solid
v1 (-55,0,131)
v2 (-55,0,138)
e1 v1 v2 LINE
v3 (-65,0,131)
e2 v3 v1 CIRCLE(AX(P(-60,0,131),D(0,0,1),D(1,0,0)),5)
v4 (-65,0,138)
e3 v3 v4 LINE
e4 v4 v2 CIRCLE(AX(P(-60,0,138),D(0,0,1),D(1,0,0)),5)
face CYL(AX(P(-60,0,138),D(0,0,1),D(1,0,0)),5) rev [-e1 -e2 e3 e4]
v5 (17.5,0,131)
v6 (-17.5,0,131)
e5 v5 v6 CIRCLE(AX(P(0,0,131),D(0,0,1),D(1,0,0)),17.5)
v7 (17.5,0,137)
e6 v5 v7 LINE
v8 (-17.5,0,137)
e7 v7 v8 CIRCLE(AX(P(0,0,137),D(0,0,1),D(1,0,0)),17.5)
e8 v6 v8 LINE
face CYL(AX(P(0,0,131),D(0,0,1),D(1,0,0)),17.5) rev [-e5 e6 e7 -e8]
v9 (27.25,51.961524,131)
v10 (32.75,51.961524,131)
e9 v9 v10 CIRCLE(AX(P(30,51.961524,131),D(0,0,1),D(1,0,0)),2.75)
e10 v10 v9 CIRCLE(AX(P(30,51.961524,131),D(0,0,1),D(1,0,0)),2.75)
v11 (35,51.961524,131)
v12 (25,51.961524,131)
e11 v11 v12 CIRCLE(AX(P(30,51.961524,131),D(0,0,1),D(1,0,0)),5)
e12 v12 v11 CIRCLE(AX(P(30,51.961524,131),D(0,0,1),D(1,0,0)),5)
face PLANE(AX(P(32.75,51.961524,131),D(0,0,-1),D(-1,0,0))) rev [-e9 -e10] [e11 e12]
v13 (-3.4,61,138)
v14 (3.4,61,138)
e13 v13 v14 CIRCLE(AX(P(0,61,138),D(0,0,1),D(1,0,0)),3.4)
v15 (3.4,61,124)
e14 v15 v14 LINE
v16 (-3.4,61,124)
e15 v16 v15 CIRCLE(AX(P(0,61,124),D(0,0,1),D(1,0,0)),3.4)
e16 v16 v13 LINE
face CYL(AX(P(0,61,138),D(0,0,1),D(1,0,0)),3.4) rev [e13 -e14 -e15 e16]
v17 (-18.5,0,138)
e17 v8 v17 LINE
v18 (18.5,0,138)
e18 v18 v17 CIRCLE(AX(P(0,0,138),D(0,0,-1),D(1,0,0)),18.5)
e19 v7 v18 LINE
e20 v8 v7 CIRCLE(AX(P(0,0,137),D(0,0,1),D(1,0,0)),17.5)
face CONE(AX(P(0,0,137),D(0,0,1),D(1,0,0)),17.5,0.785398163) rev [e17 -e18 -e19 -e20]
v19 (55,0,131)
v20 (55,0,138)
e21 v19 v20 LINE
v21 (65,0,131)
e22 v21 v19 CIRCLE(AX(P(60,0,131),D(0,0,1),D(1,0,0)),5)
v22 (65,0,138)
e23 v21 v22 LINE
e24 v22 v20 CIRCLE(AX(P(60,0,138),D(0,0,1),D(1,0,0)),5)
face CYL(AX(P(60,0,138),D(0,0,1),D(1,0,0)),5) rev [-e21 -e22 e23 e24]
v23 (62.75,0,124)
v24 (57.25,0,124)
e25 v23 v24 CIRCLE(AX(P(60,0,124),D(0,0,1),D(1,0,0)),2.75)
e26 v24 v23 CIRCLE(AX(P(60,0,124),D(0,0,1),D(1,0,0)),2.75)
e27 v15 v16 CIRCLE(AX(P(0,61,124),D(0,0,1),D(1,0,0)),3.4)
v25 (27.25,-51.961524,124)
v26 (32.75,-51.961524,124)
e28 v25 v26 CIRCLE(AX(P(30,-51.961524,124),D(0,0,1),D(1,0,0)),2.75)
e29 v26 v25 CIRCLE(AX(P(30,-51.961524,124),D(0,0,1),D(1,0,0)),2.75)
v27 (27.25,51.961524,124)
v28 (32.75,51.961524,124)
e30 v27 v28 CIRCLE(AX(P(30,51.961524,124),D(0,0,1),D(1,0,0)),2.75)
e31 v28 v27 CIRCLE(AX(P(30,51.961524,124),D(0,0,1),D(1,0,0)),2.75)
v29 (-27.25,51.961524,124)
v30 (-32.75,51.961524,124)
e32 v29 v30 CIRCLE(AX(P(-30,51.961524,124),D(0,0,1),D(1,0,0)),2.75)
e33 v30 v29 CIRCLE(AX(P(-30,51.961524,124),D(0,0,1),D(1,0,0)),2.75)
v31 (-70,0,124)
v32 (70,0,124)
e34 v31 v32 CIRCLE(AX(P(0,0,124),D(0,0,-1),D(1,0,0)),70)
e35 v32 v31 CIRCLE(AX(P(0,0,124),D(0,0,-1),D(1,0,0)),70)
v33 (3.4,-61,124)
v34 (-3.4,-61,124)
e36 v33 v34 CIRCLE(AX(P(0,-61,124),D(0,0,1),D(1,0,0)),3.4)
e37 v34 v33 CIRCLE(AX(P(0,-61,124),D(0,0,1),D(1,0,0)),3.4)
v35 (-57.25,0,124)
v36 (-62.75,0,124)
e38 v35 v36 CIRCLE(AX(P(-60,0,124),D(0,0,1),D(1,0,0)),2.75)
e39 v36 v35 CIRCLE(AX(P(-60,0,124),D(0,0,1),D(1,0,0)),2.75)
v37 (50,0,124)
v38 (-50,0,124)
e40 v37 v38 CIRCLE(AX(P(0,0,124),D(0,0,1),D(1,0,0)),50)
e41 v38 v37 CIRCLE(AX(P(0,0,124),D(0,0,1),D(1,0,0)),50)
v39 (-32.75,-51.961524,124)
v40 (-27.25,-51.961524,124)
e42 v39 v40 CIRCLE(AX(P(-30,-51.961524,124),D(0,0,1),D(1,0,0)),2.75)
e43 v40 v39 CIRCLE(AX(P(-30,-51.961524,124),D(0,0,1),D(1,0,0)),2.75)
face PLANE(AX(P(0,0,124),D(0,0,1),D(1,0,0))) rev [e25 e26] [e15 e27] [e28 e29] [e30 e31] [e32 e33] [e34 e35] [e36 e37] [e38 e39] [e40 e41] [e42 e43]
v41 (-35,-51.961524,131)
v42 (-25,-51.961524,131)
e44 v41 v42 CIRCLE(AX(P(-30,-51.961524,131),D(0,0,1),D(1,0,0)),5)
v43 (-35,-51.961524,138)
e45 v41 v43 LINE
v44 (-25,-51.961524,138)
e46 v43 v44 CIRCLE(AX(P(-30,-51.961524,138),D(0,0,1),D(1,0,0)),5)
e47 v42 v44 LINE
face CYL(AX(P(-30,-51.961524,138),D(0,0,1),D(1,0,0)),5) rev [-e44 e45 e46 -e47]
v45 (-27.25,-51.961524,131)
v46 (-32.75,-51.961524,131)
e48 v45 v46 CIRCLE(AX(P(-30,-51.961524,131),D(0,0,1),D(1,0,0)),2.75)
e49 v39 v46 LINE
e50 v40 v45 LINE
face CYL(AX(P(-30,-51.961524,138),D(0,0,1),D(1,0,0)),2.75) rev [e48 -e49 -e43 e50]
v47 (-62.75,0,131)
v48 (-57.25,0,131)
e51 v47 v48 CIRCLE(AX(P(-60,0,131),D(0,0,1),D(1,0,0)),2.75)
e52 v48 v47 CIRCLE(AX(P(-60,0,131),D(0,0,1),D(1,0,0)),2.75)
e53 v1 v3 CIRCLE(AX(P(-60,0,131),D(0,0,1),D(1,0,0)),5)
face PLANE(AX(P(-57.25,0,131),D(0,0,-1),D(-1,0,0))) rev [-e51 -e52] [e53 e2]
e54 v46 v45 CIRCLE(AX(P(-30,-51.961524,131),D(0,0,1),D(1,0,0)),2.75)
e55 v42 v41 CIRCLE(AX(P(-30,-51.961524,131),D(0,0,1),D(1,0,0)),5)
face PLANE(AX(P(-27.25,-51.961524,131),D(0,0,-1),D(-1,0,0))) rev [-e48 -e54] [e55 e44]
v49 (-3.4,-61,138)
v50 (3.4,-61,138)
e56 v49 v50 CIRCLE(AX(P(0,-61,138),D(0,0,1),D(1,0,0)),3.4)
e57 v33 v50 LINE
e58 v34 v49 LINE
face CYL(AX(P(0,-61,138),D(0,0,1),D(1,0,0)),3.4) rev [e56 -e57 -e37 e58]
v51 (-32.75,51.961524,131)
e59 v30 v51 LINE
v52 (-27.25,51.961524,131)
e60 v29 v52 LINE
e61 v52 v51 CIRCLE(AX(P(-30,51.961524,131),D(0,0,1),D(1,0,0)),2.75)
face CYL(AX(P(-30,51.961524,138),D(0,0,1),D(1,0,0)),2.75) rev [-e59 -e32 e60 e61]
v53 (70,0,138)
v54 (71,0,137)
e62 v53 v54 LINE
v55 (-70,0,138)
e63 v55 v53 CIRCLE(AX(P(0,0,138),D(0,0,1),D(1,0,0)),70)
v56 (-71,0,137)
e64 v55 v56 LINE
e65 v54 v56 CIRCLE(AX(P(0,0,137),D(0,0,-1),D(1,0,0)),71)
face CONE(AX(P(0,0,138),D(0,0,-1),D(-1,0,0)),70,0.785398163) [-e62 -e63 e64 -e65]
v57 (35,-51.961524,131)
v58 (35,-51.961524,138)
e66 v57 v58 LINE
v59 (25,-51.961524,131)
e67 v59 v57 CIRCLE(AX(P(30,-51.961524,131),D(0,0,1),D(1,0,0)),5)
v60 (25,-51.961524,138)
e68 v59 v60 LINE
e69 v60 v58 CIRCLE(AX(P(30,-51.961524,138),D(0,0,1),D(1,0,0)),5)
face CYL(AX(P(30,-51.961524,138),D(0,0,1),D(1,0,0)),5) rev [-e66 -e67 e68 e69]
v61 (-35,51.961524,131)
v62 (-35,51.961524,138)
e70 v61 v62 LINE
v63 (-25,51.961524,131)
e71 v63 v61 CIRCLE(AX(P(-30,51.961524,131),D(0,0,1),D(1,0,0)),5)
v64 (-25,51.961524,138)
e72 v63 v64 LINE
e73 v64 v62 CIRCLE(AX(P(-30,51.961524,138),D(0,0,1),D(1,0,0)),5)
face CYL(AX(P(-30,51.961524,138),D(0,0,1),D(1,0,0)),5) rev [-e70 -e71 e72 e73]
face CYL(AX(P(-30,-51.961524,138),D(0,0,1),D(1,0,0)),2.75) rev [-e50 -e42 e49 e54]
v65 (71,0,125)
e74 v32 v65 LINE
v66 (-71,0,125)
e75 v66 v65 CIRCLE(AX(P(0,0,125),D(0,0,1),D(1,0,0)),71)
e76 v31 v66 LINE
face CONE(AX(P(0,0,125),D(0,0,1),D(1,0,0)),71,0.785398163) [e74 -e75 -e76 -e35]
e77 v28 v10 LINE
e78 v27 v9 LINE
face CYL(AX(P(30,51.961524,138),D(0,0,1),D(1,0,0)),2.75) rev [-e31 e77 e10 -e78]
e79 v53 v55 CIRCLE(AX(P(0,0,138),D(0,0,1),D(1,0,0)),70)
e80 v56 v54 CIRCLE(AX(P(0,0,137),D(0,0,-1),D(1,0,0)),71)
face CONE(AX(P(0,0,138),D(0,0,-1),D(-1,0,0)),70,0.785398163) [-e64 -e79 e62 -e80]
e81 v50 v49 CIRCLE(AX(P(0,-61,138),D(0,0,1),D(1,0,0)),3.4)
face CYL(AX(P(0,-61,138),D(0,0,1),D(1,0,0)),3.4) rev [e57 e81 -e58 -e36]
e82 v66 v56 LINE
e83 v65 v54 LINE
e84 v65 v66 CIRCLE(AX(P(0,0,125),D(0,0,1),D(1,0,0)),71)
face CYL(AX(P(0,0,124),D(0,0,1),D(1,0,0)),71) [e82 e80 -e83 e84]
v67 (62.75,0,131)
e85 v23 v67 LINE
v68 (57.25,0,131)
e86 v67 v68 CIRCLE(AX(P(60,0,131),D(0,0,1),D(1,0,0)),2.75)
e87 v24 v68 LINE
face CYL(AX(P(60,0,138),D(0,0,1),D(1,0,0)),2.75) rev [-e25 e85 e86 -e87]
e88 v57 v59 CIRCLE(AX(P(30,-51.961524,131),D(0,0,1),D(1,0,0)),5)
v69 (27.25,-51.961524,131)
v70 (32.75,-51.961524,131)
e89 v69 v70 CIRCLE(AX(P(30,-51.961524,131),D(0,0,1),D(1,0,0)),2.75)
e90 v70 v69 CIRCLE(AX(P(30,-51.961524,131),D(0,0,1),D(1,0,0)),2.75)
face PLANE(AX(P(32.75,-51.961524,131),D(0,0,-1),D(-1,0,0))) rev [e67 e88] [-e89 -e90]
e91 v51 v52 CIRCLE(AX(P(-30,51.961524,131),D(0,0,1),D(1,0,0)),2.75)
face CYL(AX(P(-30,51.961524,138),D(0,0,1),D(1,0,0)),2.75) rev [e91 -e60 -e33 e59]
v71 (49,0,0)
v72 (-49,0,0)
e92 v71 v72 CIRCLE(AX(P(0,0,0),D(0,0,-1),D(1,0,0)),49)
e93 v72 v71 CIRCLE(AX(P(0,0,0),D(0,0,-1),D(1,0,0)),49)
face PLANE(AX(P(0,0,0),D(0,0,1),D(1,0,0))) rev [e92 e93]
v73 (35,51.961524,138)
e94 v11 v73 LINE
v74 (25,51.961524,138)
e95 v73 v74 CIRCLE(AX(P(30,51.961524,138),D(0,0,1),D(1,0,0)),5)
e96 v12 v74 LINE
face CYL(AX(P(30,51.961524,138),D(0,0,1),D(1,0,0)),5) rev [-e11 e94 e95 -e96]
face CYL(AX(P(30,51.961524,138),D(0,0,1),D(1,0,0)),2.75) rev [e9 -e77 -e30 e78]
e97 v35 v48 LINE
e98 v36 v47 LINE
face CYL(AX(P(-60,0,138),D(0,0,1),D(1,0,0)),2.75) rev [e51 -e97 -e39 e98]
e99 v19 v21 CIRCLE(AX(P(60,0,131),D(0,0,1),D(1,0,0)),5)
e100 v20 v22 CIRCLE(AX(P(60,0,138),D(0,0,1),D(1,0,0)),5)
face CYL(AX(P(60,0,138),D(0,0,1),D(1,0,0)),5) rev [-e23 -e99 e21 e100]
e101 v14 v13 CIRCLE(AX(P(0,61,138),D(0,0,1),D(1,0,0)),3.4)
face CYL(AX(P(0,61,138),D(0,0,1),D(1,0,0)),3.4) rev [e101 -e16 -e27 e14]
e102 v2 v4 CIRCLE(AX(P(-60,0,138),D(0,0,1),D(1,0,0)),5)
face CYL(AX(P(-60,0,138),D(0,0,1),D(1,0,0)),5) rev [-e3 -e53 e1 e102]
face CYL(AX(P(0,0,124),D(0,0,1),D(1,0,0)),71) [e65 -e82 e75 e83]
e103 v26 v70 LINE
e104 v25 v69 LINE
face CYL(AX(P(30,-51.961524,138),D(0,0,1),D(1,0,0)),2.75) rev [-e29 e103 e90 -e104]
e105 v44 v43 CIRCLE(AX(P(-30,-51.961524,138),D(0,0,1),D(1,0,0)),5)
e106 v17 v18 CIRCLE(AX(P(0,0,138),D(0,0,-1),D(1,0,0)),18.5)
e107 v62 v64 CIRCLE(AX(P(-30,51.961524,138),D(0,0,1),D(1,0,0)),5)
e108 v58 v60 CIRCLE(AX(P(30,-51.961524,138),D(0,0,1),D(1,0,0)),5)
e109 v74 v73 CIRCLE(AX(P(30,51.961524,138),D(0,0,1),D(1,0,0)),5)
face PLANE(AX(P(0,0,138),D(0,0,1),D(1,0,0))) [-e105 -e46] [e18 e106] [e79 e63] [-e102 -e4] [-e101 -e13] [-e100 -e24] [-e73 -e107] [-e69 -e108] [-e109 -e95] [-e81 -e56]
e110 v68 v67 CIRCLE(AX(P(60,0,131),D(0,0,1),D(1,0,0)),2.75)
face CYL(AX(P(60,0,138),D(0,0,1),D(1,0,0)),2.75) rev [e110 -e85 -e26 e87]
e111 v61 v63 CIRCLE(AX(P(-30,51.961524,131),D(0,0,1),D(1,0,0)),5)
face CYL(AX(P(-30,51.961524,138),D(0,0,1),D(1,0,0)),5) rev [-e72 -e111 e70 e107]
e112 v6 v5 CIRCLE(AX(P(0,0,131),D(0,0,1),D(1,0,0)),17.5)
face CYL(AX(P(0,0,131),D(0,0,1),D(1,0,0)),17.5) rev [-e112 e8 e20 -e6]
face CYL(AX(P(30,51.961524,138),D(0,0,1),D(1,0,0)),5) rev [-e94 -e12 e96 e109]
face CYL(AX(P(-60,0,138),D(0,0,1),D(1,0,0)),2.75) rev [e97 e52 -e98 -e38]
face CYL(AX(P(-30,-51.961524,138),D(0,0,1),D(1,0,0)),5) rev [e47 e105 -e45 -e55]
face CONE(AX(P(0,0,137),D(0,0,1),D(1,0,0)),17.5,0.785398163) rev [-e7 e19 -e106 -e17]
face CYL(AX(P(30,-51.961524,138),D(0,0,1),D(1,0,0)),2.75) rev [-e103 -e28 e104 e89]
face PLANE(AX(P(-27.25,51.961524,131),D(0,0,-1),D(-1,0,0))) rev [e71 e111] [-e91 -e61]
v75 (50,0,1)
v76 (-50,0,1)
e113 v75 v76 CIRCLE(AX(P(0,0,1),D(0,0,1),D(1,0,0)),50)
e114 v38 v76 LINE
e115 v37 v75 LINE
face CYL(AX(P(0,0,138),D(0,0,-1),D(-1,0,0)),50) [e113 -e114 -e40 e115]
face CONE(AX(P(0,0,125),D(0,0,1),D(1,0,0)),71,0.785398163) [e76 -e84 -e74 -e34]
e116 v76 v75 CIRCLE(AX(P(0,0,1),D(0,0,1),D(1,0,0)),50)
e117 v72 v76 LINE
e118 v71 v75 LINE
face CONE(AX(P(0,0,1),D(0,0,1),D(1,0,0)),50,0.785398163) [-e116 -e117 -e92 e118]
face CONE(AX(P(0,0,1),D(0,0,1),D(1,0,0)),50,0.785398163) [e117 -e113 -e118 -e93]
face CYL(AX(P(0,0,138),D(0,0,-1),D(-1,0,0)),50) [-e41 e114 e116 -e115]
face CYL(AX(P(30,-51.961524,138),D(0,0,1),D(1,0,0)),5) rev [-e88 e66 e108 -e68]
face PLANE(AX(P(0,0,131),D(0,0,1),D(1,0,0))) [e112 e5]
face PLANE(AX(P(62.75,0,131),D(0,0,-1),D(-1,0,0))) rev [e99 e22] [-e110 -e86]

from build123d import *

# Parameters (mm, degrees)
SKETCH1_R           = 50
BOSS_EXTRUDE1_DEPTH = 138
BOSS_EXTRUDE2_START = -14
SKETCH6_R           = 71
SKETCH6_R_2         = 50
BOSS_EXTRUDE2_DEPTH = 14
CHAMFER3_SIZE       = 1
CHAMFER4_SIZE       = 1
CHAMFER5_SIZE       = 1
SKETCH7_R           = 17.5
CUT_EXTRUDE1_DEPTH  = 7
CHAMFER6_SIZE       = 1
CIRPATTERN1_COUNT   = 6
M8_TAPPED_HOLE1_D   = 6.8


with BuildPart() as part:
    # Sketch1 → Boss-Extrude1 (new body)
    with BuildSketch(Plane.XY):
        Circle(SKETCH1_R)
    extrude(amount=BOSS_EXTRUDE1_DEPTH)

    # Sketch6 → Boss-Extrude2 (add)
    with BuildSketch(Plane.XY.offset(138).offset(BOSS_EXTRUDE2_START)):
        Circle(SKETCH6_R)
        Circle(SKETCH6_R_2, mode=Mode.SUBTRACT)
    extrude(amount=BOSS_EXTRUDE2_DEPTH)

    # Chamfer3
    chamfer3_edges = [part.edges().sort_by_distance(p)[0] for p in [
        (-50, 0, 0),
    ]]
    chamfer(chamfer3_edges, length=CHAMFER3_SIZE)

    # Chamfer4
    chamfer4_edges = [part.edges().sort_by_distance(p)[0] for p in [
        (-71, 0, 138),
    ]]
    chamfer(chamfer4_edges, length=CHAMFER4_SIZE)

    # Chamfer5
    chamfer5_edges = [part.edges().sort_by_distance(p)[0] for p in [
        (-71, 0, 124),
    ]]
    chamfer(chamfer5_edges, length=CHAMFER5_SIZE)

    # Sketch7 → Cut-Extrude1 (cut)
    with BuildSketch(Plane.XY.offset(138)):
        Circle(SKETCH7_R)
    extrude(amount=-CUT_EXTRUDE1_DEPTH, mode=Mode.SUBTRACT)

    # Chamfer6
    chamfer6_edges = [part.edges().sort_by_distance(p)[0] for p in [
        (-17.5, 0, 138),
    ]]
    chamfer(chamfer6_edges, length=CHAMFER6_SIZE)

    # Sketch9 → Hole size (per socket head cap screw type)1 (revolve, cut)
    with BuildSketch(Plane(origin=(60, 0, 138), x_dir=(0, -1, 0), z_dir=(1, 0, 0))):
        Polygon((0, 0), (0, 15.652366702), (2.75, 14), (2.75, 7), (5, 7), (5, 0), align=None)
    hole_size_per_socket_head_cap_screw_typ = revolve(axis=Axis((60, 0, 144.35), (0, 0, -1)), mode=Mode.SUBTRACT)

    # CirPattern1: Hole size (per socket head cap screw type)1 ×6 about axis
    cirpattern1_axis = Axis((0, 0, 0), (0, 0, 1))
    for i in range(1, CIRPATTERN1_COUNT):
        add(hole_size_per_socket_head_cap_screw_typ.rotate(cirpattern1_axis, i * 360 / CIRPATTERN1_COUNT), mode=Mode.SUBTRACT)

    # M8 Tapped Hole1 (through all)
    with Locations(Plane.XY.offset(138)):
        with Locations((0, 61), (0, -61)):
            Hole(M8_TAPPED_HOLE1_D / 2)


solid = part.part
